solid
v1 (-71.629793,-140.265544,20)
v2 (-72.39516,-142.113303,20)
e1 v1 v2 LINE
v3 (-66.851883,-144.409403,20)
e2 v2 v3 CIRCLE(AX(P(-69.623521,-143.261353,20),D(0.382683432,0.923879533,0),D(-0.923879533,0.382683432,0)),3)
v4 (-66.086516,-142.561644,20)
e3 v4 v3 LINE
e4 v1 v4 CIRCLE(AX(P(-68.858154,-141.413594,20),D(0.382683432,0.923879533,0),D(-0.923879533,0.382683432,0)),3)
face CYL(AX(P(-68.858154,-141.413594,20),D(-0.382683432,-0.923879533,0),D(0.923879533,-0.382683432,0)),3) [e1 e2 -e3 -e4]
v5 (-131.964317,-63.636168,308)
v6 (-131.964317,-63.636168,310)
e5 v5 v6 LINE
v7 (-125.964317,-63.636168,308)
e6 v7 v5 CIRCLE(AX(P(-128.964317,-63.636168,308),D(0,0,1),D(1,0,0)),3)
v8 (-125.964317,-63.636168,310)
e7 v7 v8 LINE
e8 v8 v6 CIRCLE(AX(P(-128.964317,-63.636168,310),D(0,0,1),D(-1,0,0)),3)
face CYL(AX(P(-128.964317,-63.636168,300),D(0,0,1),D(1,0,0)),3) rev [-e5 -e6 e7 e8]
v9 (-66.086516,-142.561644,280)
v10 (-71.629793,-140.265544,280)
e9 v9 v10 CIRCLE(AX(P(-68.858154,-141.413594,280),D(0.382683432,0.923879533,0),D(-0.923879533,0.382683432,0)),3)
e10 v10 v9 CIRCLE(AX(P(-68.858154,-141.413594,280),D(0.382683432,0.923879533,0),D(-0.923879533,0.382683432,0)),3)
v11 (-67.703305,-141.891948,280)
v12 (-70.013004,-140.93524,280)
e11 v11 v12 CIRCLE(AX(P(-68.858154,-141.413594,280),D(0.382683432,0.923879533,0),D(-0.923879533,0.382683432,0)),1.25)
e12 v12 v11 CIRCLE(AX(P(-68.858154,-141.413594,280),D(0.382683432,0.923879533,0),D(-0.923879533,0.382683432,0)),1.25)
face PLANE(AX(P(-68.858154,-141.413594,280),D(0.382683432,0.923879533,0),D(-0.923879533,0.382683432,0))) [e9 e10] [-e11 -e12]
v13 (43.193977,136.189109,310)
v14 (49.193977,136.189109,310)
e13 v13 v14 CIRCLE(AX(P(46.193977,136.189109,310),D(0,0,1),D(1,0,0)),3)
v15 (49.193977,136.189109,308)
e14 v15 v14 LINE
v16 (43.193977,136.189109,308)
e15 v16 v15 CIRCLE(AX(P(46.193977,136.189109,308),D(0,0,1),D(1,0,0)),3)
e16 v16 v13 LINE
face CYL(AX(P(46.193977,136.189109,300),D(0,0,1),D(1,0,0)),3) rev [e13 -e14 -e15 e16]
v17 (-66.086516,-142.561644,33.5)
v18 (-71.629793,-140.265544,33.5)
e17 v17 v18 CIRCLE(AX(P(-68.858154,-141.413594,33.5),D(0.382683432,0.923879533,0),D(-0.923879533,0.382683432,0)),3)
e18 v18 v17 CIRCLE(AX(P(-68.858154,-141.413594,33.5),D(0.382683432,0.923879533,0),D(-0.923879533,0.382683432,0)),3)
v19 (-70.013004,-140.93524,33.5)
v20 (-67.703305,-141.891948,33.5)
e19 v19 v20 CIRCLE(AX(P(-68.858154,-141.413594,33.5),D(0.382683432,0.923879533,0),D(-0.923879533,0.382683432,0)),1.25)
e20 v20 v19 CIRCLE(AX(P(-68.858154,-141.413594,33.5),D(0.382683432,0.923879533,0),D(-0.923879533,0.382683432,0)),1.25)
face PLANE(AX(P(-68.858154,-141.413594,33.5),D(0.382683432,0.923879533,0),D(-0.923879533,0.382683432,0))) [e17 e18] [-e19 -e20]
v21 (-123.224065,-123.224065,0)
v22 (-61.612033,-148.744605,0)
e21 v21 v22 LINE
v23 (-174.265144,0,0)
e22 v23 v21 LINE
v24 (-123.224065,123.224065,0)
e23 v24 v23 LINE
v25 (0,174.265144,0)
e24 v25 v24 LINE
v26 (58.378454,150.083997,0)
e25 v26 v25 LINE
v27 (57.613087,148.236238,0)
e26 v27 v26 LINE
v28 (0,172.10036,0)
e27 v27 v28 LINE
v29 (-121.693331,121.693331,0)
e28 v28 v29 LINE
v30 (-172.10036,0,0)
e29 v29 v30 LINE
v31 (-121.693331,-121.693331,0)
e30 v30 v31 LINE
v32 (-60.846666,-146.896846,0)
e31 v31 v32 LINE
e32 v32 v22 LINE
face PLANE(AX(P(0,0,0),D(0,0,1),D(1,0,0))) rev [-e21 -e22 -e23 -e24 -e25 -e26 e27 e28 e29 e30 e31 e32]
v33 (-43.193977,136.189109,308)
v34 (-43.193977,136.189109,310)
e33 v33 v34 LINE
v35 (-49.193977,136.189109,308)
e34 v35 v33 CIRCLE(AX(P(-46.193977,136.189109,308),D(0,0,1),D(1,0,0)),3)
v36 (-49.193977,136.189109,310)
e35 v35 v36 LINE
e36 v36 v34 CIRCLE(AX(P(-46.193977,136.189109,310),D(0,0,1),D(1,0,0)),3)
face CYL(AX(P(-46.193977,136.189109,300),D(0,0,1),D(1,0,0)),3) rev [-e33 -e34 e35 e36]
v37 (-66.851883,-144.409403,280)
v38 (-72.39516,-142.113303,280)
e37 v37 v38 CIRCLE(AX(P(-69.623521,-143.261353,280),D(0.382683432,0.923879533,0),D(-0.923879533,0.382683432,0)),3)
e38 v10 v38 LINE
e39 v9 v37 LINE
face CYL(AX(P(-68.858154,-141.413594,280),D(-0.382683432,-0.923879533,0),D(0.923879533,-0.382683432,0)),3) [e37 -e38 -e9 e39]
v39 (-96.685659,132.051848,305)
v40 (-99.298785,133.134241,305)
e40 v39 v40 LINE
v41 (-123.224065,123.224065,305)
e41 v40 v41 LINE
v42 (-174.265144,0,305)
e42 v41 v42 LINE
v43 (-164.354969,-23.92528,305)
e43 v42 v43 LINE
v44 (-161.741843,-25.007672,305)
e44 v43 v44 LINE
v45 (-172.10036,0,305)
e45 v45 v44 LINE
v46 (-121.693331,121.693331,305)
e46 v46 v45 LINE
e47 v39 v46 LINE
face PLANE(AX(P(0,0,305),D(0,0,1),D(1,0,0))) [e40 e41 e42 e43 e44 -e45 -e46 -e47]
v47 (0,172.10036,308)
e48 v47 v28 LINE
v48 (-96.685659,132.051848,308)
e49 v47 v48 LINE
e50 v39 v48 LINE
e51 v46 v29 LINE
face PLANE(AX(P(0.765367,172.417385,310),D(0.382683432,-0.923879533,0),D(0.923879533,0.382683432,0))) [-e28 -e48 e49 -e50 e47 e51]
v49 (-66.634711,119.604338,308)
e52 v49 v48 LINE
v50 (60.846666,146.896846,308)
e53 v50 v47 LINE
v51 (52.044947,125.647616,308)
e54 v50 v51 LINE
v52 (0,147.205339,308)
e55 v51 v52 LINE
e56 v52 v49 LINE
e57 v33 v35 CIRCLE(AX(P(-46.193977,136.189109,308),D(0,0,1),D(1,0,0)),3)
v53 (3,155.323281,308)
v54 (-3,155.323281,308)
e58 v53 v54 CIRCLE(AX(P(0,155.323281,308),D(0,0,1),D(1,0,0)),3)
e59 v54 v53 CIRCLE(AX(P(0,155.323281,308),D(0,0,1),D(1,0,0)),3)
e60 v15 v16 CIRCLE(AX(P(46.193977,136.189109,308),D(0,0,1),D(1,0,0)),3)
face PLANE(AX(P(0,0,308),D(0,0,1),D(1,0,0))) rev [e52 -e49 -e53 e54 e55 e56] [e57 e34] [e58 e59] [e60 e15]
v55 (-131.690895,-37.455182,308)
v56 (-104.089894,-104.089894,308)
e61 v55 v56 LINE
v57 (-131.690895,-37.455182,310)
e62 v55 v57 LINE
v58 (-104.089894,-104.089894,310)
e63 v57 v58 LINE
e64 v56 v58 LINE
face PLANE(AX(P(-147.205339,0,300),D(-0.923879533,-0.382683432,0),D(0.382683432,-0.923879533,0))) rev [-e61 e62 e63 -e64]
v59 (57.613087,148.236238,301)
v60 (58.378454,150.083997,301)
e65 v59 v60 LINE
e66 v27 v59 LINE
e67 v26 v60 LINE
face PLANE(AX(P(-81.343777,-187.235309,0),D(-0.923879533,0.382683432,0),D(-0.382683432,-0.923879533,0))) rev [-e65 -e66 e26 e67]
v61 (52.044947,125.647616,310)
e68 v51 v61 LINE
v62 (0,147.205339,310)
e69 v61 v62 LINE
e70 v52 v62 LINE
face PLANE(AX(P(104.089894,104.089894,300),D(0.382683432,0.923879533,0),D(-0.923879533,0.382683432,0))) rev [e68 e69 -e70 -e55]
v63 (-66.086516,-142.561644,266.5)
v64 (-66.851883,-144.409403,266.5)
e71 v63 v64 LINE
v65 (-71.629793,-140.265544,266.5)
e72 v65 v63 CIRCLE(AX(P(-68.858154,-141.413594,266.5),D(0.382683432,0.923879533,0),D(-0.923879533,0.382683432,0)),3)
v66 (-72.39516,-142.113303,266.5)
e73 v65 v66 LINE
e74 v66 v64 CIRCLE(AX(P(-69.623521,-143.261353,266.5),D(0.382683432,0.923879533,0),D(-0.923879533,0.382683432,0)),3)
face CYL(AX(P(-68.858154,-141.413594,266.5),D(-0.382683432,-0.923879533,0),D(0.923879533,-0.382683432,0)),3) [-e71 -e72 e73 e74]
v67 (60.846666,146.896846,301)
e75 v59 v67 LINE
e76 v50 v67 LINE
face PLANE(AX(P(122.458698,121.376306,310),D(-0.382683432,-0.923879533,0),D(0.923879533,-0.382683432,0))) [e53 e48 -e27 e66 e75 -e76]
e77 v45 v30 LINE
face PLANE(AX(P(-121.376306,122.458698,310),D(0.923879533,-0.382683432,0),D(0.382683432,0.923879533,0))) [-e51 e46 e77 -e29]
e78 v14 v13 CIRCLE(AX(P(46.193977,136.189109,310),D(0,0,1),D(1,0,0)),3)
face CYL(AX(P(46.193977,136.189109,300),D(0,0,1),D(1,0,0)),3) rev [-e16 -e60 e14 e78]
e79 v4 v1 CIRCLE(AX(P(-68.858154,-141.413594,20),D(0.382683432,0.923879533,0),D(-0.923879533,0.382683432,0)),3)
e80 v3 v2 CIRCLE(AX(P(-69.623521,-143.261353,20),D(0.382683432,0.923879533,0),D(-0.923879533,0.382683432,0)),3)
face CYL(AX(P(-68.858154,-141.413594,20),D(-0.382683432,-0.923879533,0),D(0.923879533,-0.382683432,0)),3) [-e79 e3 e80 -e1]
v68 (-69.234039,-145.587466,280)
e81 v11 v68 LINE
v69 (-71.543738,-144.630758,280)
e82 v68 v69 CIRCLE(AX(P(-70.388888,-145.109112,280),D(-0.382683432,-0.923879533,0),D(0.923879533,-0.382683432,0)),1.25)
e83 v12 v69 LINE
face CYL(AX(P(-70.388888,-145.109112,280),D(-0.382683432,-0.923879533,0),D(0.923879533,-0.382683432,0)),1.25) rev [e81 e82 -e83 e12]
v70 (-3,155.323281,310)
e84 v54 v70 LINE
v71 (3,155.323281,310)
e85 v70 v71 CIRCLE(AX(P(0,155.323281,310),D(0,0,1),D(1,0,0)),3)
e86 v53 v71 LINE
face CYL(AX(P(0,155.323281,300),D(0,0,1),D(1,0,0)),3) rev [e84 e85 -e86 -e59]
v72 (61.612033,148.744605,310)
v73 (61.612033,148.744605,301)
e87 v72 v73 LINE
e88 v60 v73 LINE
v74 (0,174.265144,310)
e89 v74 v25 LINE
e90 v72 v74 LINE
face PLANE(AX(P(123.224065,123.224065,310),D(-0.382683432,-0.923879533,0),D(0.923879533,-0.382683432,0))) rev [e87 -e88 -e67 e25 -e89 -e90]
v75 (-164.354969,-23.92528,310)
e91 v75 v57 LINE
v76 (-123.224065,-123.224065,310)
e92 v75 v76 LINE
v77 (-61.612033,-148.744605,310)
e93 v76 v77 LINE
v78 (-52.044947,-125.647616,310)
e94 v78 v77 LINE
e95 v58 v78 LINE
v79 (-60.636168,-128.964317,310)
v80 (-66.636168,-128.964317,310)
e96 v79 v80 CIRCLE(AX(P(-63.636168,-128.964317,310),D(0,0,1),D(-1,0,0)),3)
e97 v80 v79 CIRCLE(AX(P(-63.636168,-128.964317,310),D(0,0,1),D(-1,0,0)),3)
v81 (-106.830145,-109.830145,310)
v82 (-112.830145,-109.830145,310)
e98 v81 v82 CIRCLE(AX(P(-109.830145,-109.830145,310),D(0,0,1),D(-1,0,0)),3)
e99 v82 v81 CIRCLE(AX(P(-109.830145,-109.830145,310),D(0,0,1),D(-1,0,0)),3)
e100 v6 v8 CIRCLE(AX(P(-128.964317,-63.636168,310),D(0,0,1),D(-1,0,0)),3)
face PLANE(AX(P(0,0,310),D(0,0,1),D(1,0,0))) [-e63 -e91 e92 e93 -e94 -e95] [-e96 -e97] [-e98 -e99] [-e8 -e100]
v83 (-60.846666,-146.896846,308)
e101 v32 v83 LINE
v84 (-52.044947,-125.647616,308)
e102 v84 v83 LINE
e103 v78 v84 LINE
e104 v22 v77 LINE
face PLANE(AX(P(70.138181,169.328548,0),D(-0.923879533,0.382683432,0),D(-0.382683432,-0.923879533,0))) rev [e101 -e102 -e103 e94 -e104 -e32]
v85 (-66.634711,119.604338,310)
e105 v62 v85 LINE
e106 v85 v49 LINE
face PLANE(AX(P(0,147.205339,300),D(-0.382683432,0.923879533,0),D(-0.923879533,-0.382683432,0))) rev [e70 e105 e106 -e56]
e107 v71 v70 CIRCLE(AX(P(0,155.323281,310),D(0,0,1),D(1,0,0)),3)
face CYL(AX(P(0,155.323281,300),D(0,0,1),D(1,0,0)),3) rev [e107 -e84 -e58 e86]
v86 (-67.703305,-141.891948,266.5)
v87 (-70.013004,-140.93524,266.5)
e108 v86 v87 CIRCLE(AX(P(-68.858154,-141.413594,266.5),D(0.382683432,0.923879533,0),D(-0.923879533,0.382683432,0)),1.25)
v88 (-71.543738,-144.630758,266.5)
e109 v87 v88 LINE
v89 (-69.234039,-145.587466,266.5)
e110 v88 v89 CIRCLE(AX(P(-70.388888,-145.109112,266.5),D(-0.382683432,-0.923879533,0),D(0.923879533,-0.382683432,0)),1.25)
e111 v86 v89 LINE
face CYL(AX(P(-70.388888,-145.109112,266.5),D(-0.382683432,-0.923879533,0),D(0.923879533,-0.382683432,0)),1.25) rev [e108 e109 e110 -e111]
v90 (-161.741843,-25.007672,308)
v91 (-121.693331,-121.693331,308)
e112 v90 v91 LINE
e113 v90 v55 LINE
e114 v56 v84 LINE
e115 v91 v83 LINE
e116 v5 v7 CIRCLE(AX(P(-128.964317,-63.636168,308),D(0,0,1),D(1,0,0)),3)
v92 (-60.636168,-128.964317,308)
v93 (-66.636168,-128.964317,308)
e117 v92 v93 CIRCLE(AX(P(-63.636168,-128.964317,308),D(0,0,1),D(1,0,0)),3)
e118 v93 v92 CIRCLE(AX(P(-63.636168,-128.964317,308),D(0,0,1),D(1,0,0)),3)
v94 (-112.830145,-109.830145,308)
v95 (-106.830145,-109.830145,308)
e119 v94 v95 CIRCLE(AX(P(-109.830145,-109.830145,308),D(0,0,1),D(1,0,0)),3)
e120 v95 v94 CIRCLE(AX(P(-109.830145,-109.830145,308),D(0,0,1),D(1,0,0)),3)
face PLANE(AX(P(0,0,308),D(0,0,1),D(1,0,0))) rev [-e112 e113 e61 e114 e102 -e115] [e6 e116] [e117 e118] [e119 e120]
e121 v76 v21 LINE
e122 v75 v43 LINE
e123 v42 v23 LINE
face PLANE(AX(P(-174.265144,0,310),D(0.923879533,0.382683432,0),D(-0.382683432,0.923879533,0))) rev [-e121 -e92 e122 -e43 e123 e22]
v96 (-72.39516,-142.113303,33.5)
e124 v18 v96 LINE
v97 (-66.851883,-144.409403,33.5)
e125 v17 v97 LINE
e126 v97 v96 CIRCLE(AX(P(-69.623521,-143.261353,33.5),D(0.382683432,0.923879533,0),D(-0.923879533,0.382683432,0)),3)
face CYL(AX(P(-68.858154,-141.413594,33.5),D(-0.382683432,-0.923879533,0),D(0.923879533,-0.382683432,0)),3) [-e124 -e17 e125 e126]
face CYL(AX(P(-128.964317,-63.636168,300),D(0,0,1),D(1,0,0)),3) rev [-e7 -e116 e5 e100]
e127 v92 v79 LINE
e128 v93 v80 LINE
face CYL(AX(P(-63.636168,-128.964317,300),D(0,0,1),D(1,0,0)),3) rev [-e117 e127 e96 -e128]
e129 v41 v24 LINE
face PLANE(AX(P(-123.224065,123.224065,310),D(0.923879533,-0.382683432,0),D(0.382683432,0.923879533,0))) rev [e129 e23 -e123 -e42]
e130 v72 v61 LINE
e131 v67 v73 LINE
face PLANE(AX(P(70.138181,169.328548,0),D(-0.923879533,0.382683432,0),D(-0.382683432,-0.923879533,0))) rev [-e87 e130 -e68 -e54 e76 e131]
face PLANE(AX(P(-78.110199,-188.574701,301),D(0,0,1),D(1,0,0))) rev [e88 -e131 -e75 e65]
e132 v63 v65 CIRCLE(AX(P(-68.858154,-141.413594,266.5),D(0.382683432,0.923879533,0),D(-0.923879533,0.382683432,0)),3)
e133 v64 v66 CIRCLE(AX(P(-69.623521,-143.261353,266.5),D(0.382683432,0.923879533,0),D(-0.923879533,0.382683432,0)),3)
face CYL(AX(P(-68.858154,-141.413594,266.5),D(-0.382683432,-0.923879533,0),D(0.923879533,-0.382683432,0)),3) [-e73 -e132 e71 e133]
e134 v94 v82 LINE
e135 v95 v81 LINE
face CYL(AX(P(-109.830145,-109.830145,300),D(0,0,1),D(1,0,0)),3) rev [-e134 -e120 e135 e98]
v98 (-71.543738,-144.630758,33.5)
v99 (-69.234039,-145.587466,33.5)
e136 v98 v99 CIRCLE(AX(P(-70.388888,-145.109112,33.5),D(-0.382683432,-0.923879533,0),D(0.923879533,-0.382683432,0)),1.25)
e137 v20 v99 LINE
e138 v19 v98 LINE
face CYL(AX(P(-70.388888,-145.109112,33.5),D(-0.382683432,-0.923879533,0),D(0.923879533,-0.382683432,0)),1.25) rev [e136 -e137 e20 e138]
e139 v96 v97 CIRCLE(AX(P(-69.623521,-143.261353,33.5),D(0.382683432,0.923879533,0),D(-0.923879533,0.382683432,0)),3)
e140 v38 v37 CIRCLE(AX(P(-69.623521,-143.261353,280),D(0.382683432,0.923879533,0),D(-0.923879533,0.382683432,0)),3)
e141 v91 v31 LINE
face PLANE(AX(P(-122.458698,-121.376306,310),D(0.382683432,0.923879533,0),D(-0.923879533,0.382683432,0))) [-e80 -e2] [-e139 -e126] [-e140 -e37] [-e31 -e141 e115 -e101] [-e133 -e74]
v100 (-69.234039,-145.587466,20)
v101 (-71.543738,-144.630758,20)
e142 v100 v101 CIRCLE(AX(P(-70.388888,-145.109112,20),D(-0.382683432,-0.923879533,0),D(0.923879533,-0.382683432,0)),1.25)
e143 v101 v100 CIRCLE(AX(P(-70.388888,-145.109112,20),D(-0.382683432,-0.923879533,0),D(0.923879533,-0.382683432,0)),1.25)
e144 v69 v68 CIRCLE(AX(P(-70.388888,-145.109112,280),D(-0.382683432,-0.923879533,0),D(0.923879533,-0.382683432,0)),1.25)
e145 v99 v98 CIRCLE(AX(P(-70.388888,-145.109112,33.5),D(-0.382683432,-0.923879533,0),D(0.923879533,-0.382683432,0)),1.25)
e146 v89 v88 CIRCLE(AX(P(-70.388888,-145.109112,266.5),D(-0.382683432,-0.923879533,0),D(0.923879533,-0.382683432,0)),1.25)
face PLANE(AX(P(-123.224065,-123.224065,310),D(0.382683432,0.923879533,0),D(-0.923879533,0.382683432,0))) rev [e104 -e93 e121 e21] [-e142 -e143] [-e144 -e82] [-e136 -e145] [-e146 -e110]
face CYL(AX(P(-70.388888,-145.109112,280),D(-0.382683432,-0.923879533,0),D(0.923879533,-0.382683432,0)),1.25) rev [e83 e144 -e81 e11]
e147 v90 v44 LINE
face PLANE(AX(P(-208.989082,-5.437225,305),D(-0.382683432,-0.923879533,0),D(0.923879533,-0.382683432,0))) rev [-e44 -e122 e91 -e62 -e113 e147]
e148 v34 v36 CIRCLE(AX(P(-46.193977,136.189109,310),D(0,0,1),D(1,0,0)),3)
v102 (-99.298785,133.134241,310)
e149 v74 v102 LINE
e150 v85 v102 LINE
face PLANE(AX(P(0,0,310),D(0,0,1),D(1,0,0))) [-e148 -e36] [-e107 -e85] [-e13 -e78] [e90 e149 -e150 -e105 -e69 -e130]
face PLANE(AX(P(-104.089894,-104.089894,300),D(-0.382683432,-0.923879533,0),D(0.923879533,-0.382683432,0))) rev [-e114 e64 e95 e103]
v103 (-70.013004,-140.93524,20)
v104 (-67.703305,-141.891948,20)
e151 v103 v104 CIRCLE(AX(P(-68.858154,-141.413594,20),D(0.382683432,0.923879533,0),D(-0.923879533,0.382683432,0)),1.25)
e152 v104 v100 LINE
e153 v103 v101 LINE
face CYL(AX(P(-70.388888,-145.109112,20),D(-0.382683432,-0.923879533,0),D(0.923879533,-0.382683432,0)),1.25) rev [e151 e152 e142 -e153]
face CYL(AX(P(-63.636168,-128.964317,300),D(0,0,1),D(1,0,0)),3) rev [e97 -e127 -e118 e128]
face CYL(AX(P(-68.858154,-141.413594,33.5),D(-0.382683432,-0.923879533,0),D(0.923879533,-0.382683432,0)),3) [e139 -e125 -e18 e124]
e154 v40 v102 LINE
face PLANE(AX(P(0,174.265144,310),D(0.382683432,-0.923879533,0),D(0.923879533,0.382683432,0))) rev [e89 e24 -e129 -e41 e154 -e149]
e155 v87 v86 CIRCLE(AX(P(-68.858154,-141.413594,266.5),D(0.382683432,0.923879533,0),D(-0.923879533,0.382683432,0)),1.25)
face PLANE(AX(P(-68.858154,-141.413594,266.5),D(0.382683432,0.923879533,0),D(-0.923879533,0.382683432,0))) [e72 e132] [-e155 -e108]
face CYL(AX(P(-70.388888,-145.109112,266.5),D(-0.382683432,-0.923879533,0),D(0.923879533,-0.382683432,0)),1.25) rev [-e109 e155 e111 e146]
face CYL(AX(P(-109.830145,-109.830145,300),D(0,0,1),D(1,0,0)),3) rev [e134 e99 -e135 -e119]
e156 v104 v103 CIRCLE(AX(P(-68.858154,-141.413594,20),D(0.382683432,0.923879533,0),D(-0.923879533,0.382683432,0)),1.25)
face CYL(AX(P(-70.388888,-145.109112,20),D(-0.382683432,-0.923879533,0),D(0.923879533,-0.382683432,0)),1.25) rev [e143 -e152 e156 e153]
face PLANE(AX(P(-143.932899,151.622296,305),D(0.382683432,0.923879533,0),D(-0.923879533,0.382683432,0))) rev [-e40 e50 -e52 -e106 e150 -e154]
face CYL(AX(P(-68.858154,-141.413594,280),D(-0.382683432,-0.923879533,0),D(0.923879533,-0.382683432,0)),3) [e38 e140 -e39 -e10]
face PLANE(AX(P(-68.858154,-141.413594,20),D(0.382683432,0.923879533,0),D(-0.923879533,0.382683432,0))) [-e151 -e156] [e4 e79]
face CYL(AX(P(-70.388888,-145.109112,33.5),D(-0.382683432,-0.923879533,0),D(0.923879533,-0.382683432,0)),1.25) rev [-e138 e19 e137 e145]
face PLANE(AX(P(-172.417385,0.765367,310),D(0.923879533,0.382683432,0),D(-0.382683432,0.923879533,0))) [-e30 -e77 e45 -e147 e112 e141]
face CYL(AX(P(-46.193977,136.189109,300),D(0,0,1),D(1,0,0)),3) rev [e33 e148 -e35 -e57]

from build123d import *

# Parameters (mm, degrees)
BOSS_EXTRUDE1_DEPTH   = 310
SHELL1_T              = -2
CUT_EXTRUDE1_DEPTH    = 10
CUT_EXTRUDE2_DEPTH    = 397.026111511
CUT_EXTRUDE3_DEPTH    = 5
SKETCH5_R             = 3
CUT_EXTRUDE4_DEPTH    = 10
SKETCH10_R            = 3
BOSS_EXTRUDE3_DEPTH   = 2
M3_TAPPED_HOLE1_D     = 2.5
M3_TAPPED_HOLE1_DEPTH = 4
CUT_EXTRUDE5_REACH    = 492.141
SKETCH17_W            = 3.5
SKETCH17_H            = 301


with BuildPart() as part:
    # Sketch1 → Boss-Extrude1 (new body)
    with BuildSketch(Plane.XY):
        Polygon((-174.265144247, 0), (-123.224065222, -123.224065222), (0, -174.265144247), (123.224065222, -123.224065222), (174.265144247, 0), (123.224065222, 123.224065222), (0, 174.265144247), (-123.224065222, 123.224065222), align=None)
    extrude(amount=BOSS_EXTRUDE1_DEPTH)

    # Shell1
    shell1_openings = [part.faces().sort_by_distance(p)[0] for p in [
        (0, 0, 0),
    ]]
    offset(amount=SHELL1_T, openings=shell1_openings, kind=Kind.INTERSECTION)

    # Sketch2 → Cut-Extrude1 (cut)
    with BuildSketch(Plane.XY.offset(310)):
        Polygon((104.089893603, 104.089893603), (0, 147.20533924), (-104.089893603, 104.089893603), (-147.20533924, 0), (-104.089893603, -104.089893603), (0, -147.20533924), (104.089893603, -104.089893603), (147.20533924, 0), align=None)
    extrude(amount=-CUT_EXTRUDE1_DEPTH, mode=Mode.SUBTRACT)

    # Sketch3 → Cut-Extrude2 (cut, through all)
    with BuildSketch(Plane.XY.offset(310)):
        Polygon((70.138181093, 169.328548035), (-63.801020235, -154.029288344), (130.028007017, -234.315900213), (263.967208344, 89.041936166), align=None)
    extrude(amount=-CUT_EXTRUDE2_DEPTH, mode=Mode.SUBTRACT)

    # Sketch4 → Cut-Extrude3 (cut)
    with BuildSketch(Plane.XY.offset(310)):
        Polygon((-143.932898959, 151.622295845), (-51.544945707, 113.353952609), (-116.60112921, -43.705567918), (-208.989082461, -5.437224682), align=None)
    extrude(amount=-CUT_EXTRUDE3_DEPTH, mode=Mode.SUBTRACT)

    # Sketch5 → Cut-Extrude4 (cut)
    with BuildSketch(Plane.XY.offset(310)):
        with Locations((0, 155.323280742)):
            Circle(SKETCH5_R)
        with Locations((-46.193976626, 136.189109124)):
            Circle(SKETCH5_R)
        with Locations((46.193976626, 136.189109124)):
            Circle(SKETCH5_R)
        with Locations((-128.964316707, -63.636168463)):
            Circle(SKETCH5_R)
        with Locations((-109.830145089, -109.830145089)):
            Circle(SKETCH5_R)
        with Locations((-63.636168463, -128.964316707)):
            Circle(SKETCH5_R)
    extrude(amount=-CUT_EXTRUDE4_DEPTH, mode=Mode.SUBTRACT)

    # Sketch10 → Boss-Extrude3 (add)
    with BuildSketch(Plane(origin=(-60.846665746, -146.896845669, 0), x_dir=(0.9238795325112958, -0.3826834323650679, 0), z_dir=(0.3826834323650679, 0.9238795325112958, 0))):
        with Locations(Location((-9.5, -280, 0), (0, 0, 180))):
            Circle(SKETCH10_R)
        with Locations(Location((-9.5, -266.5, 0), (0, 0, 180))):
            Circle(SKETCH10_R)
        with Locations(Location((-9.5, -33.5, 0), (0, 0, 180))):
            Circle(SKETCH10_R)
        with Locations(Location((-9.5, -20, 0), (0, 0, 180))):
            Circle(SKETCH10_R)
    extrude(amount=BOSS_EXTRUDE3_DEPTH)

    # M3 Tapped Hole1
    with Locations(Plane(origin=(-61.612032611, -148.744604734, 0), x_dir=(-0.9238795325112958, 0.3826834323650679, 0), z_dir=(-0.3826834323650679, -0.9238795325112958, 0))):
        with Locations((9.5, -280), (9.5, -266.5), (9.5, -33.5), (9.5, -20)):
            Hole(M3_TAPPED_HOLE1_D / 2, depth=M3_TAPPED_HOLE1_DEPTH)

    # Sketch17 → Cut-Extrude5 (cut, up to next)
    with BuildSketch(Plane(origin=(61.612032611, 148.744604734, 0), x_dir=(0.923879532511296, -0.38268343236506785, 0), z_dir=(0.38268343236506785, 0.923879532511296, 0)), mode=Mode.PRIVATE) as cut_extrude5_sk1:
        with Locations((-1.75, -150.5)):
            Rectangle(SKETCH17_W, SKETCH17_H)
    cut_extrude5_tool1 = extrude(cut_extrude5_sk1.sketch, amount=-CUT_EXTRUDE5_REACH, mode=Mode.PRIVATE) & part.part
    add(cut_extrude5_tool1.solids().sort_by_distance((59.995243, 149.414301, 150.5))[0], mode=Mode.SUBTRACT)


solid = part.part
